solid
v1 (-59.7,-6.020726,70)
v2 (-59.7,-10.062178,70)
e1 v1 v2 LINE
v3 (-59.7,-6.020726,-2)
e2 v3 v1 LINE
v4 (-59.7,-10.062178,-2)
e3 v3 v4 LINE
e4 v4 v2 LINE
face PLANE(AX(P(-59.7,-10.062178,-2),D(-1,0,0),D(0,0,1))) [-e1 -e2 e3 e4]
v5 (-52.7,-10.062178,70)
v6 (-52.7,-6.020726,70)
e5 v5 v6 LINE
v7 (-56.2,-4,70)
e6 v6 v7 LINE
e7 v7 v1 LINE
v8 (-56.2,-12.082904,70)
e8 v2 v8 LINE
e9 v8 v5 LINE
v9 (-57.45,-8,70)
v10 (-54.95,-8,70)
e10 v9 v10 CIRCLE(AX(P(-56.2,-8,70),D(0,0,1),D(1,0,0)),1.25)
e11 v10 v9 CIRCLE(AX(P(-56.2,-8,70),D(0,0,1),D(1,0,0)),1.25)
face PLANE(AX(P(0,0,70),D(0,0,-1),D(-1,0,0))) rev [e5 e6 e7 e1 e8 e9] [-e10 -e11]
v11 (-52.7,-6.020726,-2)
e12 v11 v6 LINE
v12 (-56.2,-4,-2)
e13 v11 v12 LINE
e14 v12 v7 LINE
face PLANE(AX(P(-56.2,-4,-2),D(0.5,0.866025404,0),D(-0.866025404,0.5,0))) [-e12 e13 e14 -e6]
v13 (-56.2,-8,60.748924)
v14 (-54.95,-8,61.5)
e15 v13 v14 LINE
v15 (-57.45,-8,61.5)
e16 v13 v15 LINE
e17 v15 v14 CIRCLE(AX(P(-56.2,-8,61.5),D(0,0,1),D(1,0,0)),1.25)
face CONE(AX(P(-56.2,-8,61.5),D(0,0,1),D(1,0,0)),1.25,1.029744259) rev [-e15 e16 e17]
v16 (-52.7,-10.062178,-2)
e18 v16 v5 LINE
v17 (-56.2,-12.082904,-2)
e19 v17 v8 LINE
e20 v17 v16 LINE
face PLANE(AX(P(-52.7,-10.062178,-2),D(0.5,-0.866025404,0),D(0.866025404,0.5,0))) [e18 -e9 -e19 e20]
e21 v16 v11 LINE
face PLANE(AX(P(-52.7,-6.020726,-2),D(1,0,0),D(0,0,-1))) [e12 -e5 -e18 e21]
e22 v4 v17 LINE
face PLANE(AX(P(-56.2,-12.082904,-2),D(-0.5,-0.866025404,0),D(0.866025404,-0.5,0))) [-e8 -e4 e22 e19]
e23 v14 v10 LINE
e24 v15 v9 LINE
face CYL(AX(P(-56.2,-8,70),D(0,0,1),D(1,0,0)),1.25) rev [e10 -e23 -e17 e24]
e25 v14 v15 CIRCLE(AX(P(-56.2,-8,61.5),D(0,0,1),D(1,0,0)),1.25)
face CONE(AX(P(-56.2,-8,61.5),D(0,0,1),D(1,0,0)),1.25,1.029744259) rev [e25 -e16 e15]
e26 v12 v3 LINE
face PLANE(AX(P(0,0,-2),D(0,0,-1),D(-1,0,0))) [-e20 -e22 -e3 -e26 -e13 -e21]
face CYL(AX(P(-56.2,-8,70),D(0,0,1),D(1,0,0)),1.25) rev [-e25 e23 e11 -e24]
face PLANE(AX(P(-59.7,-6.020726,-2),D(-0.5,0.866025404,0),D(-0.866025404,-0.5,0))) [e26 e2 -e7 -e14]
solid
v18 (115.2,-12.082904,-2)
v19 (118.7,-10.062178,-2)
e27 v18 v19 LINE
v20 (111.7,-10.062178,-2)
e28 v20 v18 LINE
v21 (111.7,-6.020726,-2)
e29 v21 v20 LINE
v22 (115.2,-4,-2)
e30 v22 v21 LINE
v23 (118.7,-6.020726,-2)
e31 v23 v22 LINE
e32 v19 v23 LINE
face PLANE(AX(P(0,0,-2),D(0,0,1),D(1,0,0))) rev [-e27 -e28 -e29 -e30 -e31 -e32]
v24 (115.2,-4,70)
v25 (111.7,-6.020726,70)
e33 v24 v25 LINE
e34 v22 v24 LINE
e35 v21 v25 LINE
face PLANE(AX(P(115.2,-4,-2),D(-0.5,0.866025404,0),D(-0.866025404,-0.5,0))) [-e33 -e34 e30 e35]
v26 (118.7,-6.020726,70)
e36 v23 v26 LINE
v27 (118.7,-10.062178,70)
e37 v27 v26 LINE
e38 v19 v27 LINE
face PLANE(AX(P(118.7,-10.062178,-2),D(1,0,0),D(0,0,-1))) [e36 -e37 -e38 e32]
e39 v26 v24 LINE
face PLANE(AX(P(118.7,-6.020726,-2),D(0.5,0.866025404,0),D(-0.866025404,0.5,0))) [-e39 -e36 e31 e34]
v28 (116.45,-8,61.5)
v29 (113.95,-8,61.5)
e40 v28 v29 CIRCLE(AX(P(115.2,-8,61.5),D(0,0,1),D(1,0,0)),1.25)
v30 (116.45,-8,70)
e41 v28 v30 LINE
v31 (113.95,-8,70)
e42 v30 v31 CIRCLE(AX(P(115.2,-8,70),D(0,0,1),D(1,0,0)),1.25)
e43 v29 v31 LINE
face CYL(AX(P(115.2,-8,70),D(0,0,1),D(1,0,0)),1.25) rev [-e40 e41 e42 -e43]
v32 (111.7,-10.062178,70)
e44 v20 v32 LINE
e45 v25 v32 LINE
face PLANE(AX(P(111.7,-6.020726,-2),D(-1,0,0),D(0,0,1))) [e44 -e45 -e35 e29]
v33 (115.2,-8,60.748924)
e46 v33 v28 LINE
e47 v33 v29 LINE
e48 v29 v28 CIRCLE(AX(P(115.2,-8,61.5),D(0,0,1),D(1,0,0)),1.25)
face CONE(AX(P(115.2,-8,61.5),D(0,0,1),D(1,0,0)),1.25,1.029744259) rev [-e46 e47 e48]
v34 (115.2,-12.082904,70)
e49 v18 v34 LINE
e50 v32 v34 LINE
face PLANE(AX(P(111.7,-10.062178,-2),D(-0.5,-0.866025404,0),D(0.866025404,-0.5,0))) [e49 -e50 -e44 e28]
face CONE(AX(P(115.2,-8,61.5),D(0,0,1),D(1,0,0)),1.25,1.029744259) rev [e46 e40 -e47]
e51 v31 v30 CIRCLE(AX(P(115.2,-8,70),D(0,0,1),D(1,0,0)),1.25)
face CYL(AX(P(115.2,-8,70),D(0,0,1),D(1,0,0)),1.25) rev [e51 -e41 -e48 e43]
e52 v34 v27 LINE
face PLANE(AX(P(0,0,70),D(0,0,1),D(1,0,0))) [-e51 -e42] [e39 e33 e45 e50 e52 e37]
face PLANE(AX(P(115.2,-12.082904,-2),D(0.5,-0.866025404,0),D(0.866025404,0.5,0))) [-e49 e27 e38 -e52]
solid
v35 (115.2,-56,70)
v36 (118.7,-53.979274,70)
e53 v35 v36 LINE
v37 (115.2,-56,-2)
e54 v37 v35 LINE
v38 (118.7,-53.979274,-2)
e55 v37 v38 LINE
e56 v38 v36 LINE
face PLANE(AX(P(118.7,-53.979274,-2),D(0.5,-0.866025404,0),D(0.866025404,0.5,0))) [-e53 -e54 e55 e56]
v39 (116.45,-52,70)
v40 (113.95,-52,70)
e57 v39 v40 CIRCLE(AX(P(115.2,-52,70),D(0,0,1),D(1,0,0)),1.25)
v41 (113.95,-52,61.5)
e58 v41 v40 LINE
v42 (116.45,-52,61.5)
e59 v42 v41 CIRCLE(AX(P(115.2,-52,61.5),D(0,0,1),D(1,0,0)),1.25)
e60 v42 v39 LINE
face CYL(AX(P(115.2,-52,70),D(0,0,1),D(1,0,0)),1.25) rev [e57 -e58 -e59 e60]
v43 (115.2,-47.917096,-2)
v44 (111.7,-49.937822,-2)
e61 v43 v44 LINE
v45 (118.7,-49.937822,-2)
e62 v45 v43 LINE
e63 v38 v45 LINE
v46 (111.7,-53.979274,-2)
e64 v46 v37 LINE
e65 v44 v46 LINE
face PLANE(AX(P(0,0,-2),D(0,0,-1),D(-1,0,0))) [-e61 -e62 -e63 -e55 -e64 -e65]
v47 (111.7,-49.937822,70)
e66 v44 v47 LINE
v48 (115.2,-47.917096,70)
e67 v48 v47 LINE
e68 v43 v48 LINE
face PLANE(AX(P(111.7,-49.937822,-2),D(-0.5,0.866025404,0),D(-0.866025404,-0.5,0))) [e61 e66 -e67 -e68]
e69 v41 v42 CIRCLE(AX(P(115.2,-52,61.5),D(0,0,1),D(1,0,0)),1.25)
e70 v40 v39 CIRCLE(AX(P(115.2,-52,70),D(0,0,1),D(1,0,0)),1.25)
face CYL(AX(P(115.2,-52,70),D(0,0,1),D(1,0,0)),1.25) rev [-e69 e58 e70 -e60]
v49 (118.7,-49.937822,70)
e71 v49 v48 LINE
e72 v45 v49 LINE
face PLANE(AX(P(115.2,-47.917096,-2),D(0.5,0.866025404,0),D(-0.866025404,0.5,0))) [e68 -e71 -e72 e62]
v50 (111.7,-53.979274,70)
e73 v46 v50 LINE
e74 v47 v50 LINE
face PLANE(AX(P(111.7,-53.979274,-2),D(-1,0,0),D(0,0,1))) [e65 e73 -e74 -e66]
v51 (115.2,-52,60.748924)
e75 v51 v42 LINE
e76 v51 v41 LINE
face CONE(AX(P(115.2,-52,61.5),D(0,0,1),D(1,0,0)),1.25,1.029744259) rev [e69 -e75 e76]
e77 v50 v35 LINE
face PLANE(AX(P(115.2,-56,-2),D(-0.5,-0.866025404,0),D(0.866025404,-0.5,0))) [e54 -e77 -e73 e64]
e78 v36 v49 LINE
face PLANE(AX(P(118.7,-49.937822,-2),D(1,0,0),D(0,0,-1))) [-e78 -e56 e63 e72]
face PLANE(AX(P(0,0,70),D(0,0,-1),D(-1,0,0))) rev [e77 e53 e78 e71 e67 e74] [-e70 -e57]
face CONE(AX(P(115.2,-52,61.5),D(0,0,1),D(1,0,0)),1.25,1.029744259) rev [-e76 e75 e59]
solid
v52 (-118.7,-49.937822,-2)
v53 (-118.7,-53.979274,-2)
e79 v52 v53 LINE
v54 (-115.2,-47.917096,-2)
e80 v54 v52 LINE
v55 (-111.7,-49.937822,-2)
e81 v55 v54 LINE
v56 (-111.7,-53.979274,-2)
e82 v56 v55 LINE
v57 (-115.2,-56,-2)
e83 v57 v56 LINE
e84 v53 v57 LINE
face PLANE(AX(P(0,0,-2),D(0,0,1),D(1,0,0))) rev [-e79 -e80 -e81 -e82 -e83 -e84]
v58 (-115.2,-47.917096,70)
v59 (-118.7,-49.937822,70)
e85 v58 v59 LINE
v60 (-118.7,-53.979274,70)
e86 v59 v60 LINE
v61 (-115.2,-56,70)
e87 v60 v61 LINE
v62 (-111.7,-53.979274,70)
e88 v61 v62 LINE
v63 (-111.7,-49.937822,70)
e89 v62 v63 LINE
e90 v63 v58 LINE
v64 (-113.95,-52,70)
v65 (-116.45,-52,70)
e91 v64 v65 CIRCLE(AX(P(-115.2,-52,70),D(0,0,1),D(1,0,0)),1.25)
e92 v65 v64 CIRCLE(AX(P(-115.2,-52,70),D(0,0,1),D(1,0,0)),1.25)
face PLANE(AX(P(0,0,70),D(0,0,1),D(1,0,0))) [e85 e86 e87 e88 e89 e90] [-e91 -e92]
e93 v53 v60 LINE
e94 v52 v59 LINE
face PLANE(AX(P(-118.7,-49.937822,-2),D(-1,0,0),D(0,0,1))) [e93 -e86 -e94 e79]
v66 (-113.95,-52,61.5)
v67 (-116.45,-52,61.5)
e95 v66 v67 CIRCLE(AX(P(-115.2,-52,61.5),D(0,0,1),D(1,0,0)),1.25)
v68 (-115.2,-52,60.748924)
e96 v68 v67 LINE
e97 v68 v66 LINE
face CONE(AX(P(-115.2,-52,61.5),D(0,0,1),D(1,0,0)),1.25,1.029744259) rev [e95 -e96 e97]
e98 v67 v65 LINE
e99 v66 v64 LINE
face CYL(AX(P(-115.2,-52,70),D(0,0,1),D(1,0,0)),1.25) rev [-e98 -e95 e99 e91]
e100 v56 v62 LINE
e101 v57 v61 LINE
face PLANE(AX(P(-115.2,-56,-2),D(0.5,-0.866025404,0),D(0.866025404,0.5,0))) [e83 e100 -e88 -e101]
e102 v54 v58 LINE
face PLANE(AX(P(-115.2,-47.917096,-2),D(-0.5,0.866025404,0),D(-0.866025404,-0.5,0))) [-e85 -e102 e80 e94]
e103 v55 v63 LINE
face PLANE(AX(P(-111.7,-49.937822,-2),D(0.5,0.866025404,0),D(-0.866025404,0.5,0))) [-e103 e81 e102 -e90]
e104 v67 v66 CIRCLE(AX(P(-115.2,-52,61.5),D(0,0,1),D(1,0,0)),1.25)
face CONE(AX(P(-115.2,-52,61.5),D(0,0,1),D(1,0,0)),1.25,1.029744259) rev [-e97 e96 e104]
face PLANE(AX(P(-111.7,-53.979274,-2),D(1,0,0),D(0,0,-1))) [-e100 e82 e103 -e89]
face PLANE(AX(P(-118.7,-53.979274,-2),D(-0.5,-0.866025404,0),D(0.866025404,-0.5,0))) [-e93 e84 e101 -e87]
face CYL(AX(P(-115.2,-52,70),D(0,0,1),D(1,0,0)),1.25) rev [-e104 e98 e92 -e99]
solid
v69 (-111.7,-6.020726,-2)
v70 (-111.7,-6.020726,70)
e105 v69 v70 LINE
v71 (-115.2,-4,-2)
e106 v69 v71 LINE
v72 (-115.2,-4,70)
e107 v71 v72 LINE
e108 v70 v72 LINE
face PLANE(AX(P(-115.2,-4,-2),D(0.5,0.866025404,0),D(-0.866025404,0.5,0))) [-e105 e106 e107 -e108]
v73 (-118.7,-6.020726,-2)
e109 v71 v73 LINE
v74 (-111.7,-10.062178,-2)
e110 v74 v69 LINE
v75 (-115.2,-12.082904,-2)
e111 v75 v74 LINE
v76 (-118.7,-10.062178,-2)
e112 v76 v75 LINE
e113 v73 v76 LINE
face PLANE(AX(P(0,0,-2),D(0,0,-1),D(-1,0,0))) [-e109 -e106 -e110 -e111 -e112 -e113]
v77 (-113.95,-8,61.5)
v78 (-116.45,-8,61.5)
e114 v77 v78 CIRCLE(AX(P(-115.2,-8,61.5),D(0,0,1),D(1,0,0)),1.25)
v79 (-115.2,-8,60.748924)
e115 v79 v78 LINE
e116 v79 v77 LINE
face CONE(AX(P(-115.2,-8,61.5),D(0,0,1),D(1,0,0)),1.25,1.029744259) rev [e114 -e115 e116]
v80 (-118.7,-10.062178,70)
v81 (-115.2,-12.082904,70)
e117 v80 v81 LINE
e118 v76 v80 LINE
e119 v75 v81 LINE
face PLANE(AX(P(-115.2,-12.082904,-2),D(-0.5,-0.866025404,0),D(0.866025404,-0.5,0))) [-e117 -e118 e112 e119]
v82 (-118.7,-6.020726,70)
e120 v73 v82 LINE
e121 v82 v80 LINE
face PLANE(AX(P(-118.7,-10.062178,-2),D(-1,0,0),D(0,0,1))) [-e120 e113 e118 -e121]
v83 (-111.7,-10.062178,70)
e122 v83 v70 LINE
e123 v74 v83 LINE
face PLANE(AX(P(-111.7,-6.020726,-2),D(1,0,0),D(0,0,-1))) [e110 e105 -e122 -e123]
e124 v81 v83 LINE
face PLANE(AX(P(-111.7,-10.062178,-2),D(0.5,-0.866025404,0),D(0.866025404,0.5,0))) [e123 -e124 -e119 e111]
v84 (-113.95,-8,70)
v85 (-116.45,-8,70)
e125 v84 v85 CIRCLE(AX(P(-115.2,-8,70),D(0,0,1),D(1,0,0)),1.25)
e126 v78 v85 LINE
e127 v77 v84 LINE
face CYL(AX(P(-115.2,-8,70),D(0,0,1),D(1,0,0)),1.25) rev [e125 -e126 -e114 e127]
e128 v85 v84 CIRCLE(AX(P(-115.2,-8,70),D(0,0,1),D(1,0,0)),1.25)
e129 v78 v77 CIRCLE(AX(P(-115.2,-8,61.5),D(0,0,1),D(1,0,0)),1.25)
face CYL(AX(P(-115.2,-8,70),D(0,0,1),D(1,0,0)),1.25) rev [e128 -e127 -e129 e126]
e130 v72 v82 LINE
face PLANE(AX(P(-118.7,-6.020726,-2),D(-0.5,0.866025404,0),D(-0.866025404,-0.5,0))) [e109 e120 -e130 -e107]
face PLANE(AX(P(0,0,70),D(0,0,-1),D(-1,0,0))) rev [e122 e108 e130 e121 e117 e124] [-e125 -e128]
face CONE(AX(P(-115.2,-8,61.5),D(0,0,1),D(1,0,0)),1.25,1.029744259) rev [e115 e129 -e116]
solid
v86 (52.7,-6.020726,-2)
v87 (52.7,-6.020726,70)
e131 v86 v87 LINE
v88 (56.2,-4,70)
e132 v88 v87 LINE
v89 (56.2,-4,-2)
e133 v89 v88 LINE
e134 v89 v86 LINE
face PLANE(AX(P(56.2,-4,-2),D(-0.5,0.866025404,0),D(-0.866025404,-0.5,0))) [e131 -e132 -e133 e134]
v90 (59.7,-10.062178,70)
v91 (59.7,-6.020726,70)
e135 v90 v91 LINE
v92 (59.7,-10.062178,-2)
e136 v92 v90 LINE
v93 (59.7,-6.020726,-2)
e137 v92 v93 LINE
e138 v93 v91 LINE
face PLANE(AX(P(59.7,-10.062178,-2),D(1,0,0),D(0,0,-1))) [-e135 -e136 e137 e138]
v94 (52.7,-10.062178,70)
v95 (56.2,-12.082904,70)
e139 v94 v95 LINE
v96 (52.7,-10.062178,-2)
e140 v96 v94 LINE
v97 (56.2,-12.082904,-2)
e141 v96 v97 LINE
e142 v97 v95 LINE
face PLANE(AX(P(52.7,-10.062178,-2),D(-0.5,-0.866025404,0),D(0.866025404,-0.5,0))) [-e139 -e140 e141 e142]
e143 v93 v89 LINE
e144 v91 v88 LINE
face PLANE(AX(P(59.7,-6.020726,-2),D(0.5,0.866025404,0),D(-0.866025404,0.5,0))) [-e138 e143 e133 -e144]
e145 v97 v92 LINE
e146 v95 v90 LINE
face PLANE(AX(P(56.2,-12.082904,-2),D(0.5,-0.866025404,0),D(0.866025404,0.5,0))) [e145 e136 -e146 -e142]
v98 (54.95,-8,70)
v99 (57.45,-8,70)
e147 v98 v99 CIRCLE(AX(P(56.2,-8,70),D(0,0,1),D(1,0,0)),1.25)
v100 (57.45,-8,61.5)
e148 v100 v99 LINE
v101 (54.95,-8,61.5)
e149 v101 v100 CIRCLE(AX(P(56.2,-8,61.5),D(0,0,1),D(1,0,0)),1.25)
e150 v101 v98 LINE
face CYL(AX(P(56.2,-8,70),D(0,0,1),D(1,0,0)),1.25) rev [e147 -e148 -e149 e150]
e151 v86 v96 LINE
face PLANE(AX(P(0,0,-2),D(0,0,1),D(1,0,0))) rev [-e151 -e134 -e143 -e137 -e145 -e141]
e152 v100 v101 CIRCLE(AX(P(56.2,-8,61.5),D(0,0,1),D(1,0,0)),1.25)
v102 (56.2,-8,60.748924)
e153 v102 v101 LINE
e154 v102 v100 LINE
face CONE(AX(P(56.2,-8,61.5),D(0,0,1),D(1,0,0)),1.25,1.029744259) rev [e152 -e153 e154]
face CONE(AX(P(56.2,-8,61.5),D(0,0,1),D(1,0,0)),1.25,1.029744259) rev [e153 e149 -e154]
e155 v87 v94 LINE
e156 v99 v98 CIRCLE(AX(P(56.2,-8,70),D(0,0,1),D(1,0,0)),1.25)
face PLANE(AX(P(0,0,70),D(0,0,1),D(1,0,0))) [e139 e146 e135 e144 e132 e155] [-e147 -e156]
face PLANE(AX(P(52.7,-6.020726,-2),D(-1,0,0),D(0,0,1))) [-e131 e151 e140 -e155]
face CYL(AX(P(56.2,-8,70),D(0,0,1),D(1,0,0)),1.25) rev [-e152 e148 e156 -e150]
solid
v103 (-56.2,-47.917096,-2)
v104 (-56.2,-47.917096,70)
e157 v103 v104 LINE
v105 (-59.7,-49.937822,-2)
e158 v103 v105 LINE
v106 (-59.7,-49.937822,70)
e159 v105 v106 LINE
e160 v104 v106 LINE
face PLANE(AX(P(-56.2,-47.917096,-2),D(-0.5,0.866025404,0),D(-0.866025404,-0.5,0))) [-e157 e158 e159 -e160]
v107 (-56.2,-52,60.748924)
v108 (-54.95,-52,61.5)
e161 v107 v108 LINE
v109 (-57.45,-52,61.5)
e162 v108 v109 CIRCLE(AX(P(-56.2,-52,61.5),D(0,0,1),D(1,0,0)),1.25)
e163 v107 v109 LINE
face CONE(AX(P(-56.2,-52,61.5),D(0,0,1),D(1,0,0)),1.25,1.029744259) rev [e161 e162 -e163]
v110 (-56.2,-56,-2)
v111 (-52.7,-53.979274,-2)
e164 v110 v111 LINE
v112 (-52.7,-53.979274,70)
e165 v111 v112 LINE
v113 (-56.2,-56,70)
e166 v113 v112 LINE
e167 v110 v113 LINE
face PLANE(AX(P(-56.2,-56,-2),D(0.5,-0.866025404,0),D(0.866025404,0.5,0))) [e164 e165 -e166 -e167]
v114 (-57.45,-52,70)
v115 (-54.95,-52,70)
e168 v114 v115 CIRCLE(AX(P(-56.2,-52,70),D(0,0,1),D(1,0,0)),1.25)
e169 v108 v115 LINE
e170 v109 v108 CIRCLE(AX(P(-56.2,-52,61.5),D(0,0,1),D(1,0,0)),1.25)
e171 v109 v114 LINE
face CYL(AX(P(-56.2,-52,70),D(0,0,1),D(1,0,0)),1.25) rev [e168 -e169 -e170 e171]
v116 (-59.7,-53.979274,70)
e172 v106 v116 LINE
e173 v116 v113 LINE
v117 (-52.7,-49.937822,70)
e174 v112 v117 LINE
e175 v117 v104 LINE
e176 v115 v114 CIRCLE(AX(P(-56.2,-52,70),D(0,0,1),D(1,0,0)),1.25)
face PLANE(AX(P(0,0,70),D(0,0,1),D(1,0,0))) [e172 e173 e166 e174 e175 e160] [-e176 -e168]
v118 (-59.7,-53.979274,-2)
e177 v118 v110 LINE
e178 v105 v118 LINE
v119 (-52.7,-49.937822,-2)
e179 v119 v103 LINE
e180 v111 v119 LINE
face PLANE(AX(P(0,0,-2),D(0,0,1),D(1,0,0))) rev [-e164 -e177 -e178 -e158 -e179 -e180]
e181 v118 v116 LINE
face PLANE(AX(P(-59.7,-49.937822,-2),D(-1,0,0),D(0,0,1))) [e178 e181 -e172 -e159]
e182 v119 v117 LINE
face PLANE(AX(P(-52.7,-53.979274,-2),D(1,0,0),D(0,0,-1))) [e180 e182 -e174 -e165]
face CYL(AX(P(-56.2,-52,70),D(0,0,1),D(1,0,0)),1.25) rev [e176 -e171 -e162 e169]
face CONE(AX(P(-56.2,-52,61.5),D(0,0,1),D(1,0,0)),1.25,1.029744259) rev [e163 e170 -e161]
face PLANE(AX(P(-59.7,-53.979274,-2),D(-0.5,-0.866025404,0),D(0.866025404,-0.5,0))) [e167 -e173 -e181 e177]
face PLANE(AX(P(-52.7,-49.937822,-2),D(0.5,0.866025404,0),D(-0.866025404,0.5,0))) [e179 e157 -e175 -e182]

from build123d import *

# Parameters (mm, degrees)
BOSS_EXTRUDE1_DEPTH        = 70
BOSS_EXTRUDE1_DEPTH_BACK   = 2
BOSS_EXTRUDE1_2_DEPTH      = 70
BOSS_EXTRUDE1_2_DEPTH_BACK = 2
BOSS_EXTRUDE1_3_DEPTH      = 70
BOSS_EXTRUDE1_3_DEPTH_BACK = 2
BOSS_EXTRUDE1_4_DEPTH      = 70
BOSS_EXTRUDE1_4_DEPTH_BACK = 2
BOSS_EXTRUDE1_5_DEPTH      = 70
BOSS_EXTRUDE1_5_DEPTH_BACK = 2
BOSS_EXTRUDE1_6_DEPTH      = 70
BOSS_EXTRUDE1_6_DEPTH_BACK = 2
BOSS_EXTRUDE1_7_DEPTH      = 70
BOSS_EXTRUDE1_7_DEPTH_BACK = 2
M3_TAPPED_HOLE1_AT_2_COUNT = 2
M3_TAPPED_HOLE1_AT_2_PITCH = 44
M3_TAPPED_HOLE1_AT_3_COUNT = 2
M3_TAPPED_HOLE1_AT_3_PITCH = 73.600271739
M3_TAPPED_HOLE1_AT_4_COUNT = 2
M3_TAPPED_HOLE1_AT_4_PITCH = 59
M3_TAPPED_HOLE1_AT_5_COUNT = 2
M3_TAPPED_HOLE1_AT_5_PITCH = 176.957509024
M3_TAPPED_HOLE1_AT_6_COUNT = 2
M3_TAPPED_HOLE1_AT_6_PITCH = 234.563765318
M3_TAPPED_HOLE1_AT_7_COUNT = 2
M3_TAPPED_HOLE1_AT_7_PITCH = 230.4


with BuildPart() as part:
    # Sketch1 → Boss-Extrude1 (new, two sides: drawn at the far end of the back side and taken through both)
    with BuildSketch(Plane.XY.offset(-BOSS_EXTRUDE1_DEPTH_BACK)):
        Polygon((118.7, -6.020725942), (115.2, -4), (111.7, -6.020725942), (111.7, -10.062177826), (115.2, -12.082903769), (118.7, -10.062177826), align=None)
    extrude(amount=BOSS_EXTRUDE1_DEPTH + BOSS_EXTRUDE1_DEPTH_BACK)


with BuildPart() as body_2:
    # Sketch1 → Boss-Extrude1 2 (new, two sides: drawn at the far end of the back side and taken through both)
    with BuildSketch(Plane.XY.offset(-BOSS_EXTRUDE1_2_DEPTH_BACK)):
        Polygon((59.7, -6.020725942), (56.2, -4), (52.7, -6.020725942), (52.7, -10.062177826), (56.2, -12.082903769), (59.7, -10.062177826), align=None)
    extrude(amount=BOSS_EXTRUDE1_2_DEPTH + BOSS_EXTRUDE1_2_DEPTH_BACK)


with BuildPart() as body_3:
    # Sketch1 → Boss-Extrude1 3 (new, two sides: drawn at the far end of the back side and taken through both)
    with BuildSketch(Plane.XY.offset(-BOSS_EXTRUDE1_3_DEPTH_BACK)):
        Polygon((118.7, -49.937822174), (118.7, -53.979274058), (115.2, -56), (111.7, -53.979274058), (111.7, -49.937822174), (115.2, -47.917096231), align=None)
    extrude(amount=BOSS_EXTRUDE1_3_DEPTH + BOSS_EXTRUDE1_3_DEPTH_BACK)


with BuildPart() as body_4:
    # Sketch1 → Boss-Extrude1 4 (new, two sides: drawn at the far end of the back side and taken through both)
    with BuildSketch(Plane.XY.offset(-BOSS_EXTRUDE1_4_DEPTH_BACK)):
        Polygon((-118.7, -53.979274058), (-115.2, -56), (-111.7, -53.979274058), (-111.7, -49.937822174), (-115.2, -47.917096231), (-118.7, -49.937822174), align=None)
    extrude(amount=BOSS_EXTRUDE1_4_DEPTH + BOSS_EXTRUDE1_4_DEPTH_BACK)

    # Sketch3 → M3 Tapped Hole1 (revolve, cut)
    with BuildSketch(Plane(origin=(-115.2, -52, 70), x_dir=(0, -1, 0), z_dir=(1, 0, 0))):
        Polygon((0, 0), (0, 9.251075774), (1.25, 8.5), (1.25, 0), align=None)
    m3_tapped_hole1 = revolve(axis=Axis((-115.2, -52, 76.35), (0, 0, -1)), mode=Mode.SUBTRACT)


with BuildPart() as body_5:
    # Sketch1 → Boss-Extrude1 5 (new, two sides: drawn at the far end of the back side and taken through both)
    with BuildSketch(Plane.XY.offset(-BOSS_EXTRUDE1_5_DEPTH_BACK)):
        Polygon((-118.7, -10.062177826), (-118.7, -6.020725942), (-115.2, -4), (-111.7, -6.020725942), (-111.7, -10.062177826), (-115.2, -12.082903769), align=None)
    extrude(amount=BOSS_EXTRUDE1_5_DEPTH + BOSS_EXTRUDE1_5_DEPTH_BACK)

    # M3 Tapped Hole1 at 2: M3 Tapped Hole1 ×2
    with Locations(*[(0, i * M3_TAPPED_HOLE1_AT_2_PITCH, 0) for i in range(1, M3_TAPPED_HOLE1_AT_2_COUNT)]):
        add(m3_tapped_hole1, mode=Mode.SUBTRACT)


with BuildPart() as body_6:
    # Sketch1 → Boss-Extrude1 6 (new, two sides: drawn at the far end of the back side and taken through both)
    with BuildSketch(Plane.XY.offset(-BOSS_EXTRUDE1_6_DEPTH_BACK)):
        Polygon((-59.7, -10.062177826), (-59.7, -6.020725942), (-56.2, -4), (-52.7, -6.020725942), (-52.7, -10.062177826), (-56.2, -12.082903769), align=None)
    extrude(amount=BOSS_EXTRUDE1_6_DEPTH + BOSS_EXTRUDE1_6_DEPTH_BACK)

    # M3 Tapped Hole1 at 3: M3 Tapped Hole1 ×2
    with Locations(*[Vector(0.8016274750930587, 0.5978238797304166, 0) * (i * M3_TAPPED_HOLE1_AT_3_PITCH) for i in range(1, M3_TAPPED_HOLE1_AT_3_COUNT)]):
        add(m3_tapped_hole1, mode=Mode.SUBTRACT)


with BuildPart() as body_7:
    # Sketch1 → Boss-Extrude1 7 (new, two sides: drawn at the far end of the back side and taken through both)
    with BuildSketch(Plane.XY.offset(-BOSS_EXTRUDE1_7_DEPTH_BACK)):
        Polygon((-59.7, -53.979274058), (-56.2, -56), (-52.7, -53.979274058), (-52.7, -49.937822174), (-56.2, -47.917096231), (-59.7, -49.937822174), align=None)
    extrude(amount=BOSS_EXTRUDE1_7_DEPTH + BOSS_EXTRUDE1_7_DEPTH_BACK)

    # M3 Tapped Hole1 at 4: M3 Tapped Hole1 ×2
    with Locations(*[(i * M3_TAPPED_HOLE1_AT_4_PITCH, 0, 0) for i in range(1, M3_TAPPED_HOLE1_AT_4_COUNT)]):
        add(m3_tapped_hole1, mode=Mode.SUBTRACT)


with BuildPart() as body_2_1:
    add(body_2.part)

    # M3 Tapped Hole1 at 5: M3 Tapped Hole1 ×2
    with Locations(*[Vector(0.9685941045694556, 0.24864726138305773, 0) * (i * M3_TAPPED_HOLE1_AT_5_PITCH) for i in range(1, M3_TAPPED_HOLE1_AT_5_COUNT)]):
        add(m3_tapped_hole1, mode=Mode.SUBTRACT)


with BuildPart() as part_1:
    add(part.part)

    # M3 Tapped Hole1 at 6: M3 Tapped Hole1 ×2
    with Locations(*[Vector(0.9822488980255548, 0.1875822548312693, 0) * (i * M3_TAPPED_HOLE1_AT_6_PITCH) for i in range(1, M3_TAPPED_HOLE1_AT_6_COUNT)]):
        add(m3_tapped_hole1, mode=Mode.SUBTRACT)


with BuildPart() as body_3_1:
    add(body_3.part)

    # M3 Tapped Hole1 at 7: M3 Tapped Hole1 ×2
    with Locations(*[(i * M3_TAPPED_HOLE1_AT_7_PITCH, 0, 0) for i in range(1, M3_TAPPED_HOLE1_AT_7_COUNT)]):
        add(m3_tapped_hole1, mode=Mode.SUBTRACT)


solid = Compound([body_4.part, body_5.part, body_6.part, body_7.part, body_2_1.part, part_1.part, body_3_1.part])
